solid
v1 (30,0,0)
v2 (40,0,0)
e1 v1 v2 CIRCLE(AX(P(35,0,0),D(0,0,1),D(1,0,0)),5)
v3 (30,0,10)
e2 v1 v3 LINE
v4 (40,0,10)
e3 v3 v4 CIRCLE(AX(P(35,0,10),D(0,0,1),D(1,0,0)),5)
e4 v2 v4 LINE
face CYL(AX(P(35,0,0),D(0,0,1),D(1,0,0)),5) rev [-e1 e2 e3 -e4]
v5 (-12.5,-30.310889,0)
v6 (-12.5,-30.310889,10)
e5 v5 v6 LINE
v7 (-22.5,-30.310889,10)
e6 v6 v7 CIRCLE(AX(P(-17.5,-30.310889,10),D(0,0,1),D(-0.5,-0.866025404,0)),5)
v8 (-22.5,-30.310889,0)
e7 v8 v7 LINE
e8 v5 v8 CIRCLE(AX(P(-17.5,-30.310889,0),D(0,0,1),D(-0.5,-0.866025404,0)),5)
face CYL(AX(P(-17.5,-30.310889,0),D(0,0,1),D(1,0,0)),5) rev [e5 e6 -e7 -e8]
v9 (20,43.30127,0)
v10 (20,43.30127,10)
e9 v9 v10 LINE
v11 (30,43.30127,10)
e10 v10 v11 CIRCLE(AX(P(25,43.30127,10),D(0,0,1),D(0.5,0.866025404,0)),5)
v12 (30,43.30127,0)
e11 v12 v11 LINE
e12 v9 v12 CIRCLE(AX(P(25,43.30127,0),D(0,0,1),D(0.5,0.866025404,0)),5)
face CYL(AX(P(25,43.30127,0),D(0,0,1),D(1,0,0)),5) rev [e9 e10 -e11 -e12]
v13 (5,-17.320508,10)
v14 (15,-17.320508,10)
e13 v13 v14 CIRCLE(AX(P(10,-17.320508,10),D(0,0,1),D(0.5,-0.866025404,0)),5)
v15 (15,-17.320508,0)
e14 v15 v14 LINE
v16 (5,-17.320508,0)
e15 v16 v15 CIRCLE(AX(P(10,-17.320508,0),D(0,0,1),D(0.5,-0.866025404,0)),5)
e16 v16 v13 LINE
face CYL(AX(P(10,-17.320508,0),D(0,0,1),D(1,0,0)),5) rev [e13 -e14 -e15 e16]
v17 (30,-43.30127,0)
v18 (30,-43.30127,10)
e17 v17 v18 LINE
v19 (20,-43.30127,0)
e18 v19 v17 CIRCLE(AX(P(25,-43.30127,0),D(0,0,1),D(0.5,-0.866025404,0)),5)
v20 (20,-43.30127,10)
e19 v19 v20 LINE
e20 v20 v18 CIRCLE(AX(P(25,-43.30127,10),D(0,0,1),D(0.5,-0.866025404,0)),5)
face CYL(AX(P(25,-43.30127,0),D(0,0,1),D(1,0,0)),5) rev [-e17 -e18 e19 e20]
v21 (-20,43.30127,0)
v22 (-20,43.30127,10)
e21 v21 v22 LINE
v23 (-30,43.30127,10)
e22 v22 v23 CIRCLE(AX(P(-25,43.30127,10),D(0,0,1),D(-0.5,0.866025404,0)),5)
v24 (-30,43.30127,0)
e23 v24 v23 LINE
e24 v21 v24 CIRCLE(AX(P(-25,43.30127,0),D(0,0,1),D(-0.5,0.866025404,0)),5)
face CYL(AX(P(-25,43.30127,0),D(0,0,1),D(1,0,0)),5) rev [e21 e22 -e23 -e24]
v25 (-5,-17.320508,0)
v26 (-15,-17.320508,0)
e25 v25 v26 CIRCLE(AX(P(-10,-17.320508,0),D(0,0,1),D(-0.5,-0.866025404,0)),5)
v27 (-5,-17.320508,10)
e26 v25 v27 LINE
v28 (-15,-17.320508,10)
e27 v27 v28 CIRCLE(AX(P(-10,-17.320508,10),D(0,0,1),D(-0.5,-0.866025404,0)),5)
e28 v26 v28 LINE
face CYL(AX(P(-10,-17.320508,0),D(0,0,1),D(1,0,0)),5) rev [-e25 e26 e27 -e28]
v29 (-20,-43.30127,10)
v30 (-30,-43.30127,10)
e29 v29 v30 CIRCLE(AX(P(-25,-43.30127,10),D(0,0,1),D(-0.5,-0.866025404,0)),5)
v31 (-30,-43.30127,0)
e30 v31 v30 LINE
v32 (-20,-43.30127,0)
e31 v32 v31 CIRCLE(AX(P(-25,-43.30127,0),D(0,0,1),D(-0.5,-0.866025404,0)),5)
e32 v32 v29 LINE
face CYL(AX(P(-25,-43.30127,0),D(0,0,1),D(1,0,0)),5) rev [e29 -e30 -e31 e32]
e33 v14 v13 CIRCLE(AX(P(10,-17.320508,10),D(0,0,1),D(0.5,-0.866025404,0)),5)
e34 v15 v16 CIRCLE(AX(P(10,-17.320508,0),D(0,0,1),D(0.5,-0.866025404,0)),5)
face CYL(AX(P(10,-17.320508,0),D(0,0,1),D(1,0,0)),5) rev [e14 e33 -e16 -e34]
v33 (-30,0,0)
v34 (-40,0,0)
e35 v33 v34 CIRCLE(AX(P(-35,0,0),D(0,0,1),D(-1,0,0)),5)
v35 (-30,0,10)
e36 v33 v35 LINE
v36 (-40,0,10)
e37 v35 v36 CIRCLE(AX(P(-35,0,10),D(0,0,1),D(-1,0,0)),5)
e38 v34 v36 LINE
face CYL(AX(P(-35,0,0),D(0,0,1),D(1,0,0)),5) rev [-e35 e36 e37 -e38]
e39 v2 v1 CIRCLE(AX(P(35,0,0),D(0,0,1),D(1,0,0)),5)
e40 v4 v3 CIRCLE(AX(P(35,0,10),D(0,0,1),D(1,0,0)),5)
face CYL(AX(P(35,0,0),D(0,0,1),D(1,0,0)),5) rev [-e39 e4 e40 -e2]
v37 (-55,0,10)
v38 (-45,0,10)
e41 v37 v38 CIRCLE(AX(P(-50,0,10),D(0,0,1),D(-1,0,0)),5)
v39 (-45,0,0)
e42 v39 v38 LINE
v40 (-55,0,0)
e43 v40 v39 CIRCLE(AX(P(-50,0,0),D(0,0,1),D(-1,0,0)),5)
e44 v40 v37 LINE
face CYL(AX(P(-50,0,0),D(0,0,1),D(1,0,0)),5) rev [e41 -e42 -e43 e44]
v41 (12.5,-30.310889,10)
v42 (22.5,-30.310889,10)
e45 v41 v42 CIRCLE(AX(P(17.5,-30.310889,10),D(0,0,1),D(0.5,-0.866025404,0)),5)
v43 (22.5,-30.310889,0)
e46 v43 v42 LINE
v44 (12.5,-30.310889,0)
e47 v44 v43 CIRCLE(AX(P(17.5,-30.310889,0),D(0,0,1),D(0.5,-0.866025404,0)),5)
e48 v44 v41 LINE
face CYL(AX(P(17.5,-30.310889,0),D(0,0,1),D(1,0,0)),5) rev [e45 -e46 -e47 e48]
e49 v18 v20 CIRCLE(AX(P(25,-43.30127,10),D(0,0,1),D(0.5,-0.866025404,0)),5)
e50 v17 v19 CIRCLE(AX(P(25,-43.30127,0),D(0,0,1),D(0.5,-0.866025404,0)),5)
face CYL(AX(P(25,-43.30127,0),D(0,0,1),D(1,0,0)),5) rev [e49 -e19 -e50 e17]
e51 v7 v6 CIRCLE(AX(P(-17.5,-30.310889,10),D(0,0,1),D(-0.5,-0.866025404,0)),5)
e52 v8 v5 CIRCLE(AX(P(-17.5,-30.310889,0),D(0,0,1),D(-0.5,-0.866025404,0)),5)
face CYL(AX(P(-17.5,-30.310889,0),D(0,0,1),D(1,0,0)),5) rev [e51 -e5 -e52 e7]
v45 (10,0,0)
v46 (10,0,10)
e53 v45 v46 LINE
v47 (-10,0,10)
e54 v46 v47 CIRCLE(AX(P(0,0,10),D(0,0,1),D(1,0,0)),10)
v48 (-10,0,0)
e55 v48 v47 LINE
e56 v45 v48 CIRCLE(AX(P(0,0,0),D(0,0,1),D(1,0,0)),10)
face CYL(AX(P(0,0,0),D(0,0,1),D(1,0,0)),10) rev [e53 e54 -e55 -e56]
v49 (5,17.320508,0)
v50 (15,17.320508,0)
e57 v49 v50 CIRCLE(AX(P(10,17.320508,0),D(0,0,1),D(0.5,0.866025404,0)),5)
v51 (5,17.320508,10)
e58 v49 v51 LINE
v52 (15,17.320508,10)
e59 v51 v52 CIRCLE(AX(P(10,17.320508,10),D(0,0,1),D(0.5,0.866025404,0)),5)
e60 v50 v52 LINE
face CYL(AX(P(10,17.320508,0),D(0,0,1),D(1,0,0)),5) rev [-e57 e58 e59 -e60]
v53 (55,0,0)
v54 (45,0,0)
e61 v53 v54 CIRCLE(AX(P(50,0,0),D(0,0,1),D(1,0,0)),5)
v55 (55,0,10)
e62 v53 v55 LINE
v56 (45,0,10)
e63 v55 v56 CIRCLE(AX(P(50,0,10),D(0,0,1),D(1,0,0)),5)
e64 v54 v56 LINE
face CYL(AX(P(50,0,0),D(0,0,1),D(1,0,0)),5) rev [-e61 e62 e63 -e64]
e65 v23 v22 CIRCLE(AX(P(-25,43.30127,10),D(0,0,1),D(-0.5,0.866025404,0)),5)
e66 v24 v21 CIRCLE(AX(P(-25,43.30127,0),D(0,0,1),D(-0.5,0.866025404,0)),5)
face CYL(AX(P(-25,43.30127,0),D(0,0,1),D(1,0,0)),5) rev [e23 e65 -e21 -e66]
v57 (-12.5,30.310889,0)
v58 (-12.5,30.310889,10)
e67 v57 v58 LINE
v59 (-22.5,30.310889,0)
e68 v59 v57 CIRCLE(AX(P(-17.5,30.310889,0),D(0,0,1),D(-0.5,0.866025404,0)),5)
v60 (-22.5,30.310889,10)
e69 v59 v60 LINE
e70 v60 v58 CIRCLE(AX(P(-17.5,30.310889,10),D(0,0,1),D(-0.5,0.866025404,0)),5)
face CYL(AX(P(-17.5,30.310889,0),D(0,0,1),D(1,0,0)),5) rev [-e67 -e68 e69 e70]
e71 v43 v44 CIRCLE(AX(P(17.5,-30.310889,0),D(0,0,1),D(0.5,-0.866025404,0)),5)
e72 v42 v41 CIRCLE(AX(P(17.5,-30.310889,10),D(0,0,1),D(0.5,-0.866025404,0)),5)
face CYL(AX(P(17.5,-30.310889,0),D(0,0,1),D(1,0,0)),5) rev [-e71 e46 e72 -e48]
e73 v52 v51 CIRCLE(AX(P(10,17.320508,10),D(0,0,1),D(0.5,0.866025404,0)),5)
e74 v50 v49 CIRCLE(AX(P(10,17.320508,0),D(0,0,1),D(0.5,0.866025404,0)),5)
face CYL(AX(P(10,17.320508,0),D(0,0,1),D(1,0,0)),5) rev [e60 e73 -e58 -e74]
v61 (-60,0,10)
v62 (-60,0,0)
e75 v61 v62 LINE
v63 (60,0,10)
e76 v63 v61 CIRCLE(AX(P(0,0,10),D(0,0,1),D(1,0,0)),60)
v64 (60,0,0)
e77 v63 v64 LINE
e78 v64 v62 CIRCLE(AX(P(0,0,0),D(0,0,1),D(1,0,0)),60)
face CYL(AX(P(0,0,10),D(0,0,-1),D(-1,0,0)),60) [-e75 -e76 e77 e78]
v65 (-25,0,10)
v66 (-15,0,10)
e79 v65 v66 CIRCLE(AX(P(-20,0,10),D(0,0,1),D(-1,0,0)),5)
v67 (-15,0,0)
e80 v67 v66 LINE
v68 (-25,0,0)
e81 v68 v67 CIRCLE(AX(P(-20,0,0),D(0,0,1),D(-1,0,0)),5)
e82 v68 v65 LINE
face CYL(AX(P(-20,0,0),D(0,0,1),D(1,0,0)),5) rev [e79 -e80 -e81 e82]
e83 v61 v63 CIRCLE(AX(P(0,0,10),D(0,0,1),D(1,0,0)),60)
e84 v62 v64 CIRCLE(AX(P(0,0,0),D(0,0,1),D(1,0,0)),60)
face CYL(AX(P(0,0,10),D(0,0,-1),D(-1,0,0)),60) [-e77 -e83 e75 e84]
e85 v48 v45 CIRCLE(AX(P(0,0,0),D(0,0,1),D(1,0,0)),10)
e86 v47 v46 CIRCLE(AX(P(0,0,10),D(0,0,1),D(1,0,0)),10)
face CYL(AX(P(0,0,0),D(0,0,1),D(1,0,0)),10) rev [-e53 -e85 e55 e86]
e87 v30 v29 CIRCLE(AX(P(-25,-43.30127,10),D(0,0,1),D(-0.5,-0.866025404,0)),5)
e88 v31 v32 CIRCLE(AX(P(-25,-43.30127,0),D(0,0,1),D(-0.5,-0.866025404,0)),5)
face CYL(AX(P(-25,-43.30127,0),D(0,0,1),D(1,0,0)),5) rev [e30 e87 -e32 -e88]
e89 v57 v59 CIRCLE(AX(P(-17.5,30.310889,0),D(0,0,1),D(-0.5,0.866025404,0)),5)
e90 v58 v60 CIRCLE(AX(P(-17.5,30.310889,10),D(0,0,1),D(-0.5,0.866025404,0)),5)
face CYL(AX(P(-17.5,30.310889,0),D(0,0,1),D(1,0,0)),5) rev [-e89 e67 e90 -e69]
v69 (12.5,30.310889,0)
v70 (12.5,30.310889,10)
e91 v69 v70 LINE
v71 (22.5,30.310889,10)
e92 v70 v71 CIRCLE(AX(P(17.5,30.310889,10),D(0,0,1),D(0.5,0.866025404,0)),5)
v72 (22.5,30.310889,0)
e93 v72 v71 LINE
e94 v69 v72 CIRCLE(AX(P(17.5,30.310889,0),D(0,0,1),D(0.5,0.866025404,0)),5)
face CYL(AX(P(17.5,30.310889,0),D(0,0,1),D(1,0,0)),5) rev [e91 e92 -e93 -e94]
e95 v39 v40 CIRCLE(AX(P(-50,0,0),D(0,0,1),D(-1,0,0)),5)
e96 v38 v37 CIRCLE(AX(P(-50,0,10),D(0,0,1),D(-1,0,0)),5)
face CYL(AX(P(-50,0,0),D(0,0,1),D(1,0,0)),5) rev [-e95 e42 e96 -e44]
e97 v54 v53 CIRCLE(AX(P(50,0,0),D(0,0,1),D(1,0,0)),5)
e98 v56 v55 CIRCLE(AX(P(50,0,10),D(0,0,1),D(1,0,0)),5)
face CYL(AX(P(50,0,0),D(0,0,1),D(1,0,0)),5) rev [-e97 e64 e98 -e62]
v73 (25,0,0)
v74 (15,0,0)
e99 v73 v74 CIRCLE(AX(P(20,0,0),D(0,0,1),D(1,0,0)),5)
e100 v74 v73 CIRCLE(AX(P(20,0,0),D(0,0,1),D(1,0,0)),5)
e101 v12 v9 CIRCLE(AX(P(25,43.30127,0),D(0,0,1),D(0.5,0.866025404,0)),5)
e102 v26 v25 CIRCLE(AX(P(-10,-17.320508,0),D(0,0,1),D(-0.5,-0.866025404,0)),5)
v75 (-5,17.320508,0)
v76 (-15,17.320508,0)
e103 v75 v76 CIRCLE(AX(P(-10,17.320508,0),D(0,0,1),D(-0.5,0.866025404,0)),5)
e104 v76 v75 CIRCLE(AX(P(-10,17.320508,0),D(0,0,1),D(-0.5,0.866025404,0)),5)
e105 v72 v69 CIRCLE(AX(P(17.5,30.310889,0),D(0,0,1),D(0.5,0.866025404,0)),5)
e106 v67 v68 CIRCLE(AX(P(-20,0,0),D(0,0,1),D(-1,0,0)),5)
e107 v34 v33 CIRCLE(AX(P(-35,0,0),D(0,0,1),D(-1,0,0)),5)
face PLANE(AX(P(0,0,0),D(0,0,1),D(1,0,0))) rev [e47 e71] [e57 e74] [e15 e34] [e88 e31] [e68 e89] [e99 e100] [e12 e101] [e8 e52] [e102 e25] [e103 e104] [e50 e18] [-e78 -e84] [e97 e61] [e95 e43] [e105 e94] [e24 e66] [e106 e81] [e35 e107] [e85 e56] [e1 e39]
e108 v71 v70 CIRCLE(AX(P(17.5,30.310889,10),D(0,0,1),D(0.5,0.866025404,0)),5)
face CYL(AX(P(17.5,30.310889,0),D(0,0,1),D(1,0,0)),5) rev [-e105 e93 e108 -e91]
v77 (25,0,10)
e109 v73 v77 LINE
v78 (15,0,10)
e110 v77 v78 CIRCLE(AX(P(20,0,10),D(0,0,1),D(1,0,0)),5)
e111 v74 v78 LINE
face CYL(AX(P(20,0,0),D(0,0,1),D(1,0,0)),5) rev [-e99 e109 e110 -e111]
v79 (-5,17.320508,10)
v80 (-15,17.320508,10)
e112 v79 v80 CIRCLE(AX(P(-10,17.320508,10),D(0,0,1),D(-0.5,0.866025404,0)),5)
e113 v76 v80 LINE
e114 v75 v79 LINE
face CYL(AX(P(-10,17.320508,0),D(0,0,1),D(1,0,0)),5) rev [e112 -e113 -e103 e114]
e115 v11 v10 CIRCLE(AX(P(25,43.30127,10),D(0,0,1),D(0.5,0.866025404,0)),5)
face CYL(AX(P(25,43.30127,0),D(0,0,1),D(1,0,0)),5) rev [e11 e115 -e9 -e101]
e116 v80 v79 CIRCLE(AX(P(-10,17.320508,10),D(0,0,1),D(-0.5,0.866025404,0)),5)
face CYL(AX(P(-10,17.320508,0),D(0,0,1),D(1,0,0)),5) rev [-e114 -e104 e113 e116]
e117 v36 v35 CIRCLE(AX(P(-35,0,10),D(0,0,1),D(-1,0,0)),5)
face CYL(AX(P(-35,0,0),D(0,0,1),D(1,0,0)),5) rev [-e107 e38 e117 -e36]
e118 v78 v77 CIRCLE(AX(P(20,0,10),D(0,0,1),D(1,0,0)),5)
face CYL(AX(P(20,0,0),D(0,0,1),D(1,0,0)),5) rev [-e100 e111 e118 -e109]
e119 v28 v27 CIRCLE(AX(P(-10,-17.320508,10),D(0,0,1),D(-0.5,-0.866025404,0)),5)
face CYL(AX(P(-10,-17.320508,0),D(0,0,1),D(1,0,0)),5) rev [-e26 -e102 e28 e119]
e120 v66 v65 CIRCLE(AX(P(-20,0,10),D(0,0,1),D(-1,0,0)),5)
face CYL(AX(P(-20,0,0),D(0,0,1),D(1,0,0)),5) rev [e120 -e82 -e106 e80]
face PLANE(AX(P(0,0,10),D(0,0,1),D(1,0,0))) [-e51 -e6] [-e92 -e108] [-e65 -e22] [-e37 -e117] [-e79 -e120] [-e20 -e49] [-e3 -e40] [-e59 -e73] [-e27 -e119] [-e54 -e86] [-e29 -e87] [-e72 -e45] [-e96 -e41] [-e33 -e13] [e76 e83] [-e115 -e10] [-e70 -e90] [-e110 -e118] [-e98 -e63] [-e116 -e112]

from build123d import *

# Parameters (mm, degrees)
FLANGE_OUTLINE_120_R                 = 60
FLANGE_DISC_DEPTH                    = 10
CENTRE_BORE_PROFILE_20_R             = 10
CENTRE_BORE_20_DEPTH                 = 10
SEED_HOLE_PROFILE_10_R               = 5
SEED_HOLE_10_DEPTH                   = 10
SEED_HOLE_CIRCULAR_PATTERN_6X_COUNT  = 6
RADIAL_HOLE_ROW_3X_COUNT             = 3
RADIAL_HOLE_ROW_3X_PITCH             = 15
RADIAL_HOLE_ROWS_6X_COPY_1_SKETCH_R  = 5
RADIAL_HOLE_ROWS_6X_COPY_1_DEPTH     = 10
RADIAL_HOLE_ROWS_6X_COPY_2_SKETCH_R  = 5
RADIAL_HOLE_ROWS_6X_COPY_2_DEPTH     = 10
RADIAL_HOLE_ROWS_6X_COPY_3_SKETCH_R  = 5
RADIAL_HOLE_ROWS_6X_COPY_3_DEPTH     = 10
RADIAL_HOLE_ROWS_6X_COPY_4_SKETCH_R  = 5
RADIAL_HOLE_ROWS_6X_COPY_4_DEPTH     = 10
RADIAL_HOLE_ROWS_6X_COPY_5_SKETCH_R  = 5
RADIAL_HOLE_ROWS_6X_COPY_5_DEPTH     = 10
RADIAL_HOLE_ROWS_6X_COPY_6_SKETCH_R  = 5
RADIAL_HOLE_ROWS_6X_COPY_6_DEPTH     = 10
RADIAL_HOLE_ROWS_6X_COPY_7_SKETCH_R  = 5
RADIAL_HOLE_ROWS_6X_COPY_7_DEPTH     = 10
RADIAL_HOLE_ROWS_6X_COPY_8_SKETCH_R  = 5
RADIAL_HOLE_ROWS_6X_COPY_8_DEPTH     = 10
RADIAL_HOLE_ROWS_6X_COPY_9_SKETCH_R  = 5
RADIAL_HOLE_ROWS_6X_COPY_9_DEPTH     = 10
RADIAL_HOLE_ROWS_6X_COPY_10_SKETCH_R = 5
RADIAL_HOLE_ROWS_6X_COPY_10_DEPTH    = 10
RADIAL_HOLE_ROWS_6X_COPY_11_SKETCH_R = 5
RADIAL_HOLE_ROWS_6X_COPY_11_DEPTH    = 10
RADIAL_HOLE_ROWS_6X_COPY_12_SKETCH_R = 5
RADIAL_HOLE_ROWS_6X_COPY_12_DEPTH    = 10
RADIAL_HOLE_ROWS_6X_COPY_13_SKETCH_R = 5
RADIAL_HOLE_ROWS_6X_COPY_13_DEPTH    = 10
RADIAL_HOLE_ROWS_6X_COPY_14_SKETCH_R = 5
RADIAL_HOLE_ROWS_6X_COPY_14_DEPTH    = 10
RADIAL_HOLE_ROWS_6X_COPY_15_SKETCH_R = 5
RADIAL_HOLE_ROWS_6X_COPY_15_DEPTH    = 10


with BuildPart() as part:
    # Flange Outline Ø120 → Flange Disc (new body)
    with BuildSketch(Plane.XY):
        Circle(FLANGE_OUTLINE_120_R)
    extrude(amount=FLANGE_DISC_DEPTH)

    # Centre Bore Profile Ø20 → Centre Bore Ø20 (cut)
    with BuildSketch(Plane.XY.offset(10)):
        Circle(CENTRE_BORE_PROFILE_20_R)
    extrude(amount=-CENTRE_BORE_20_DEPTH, mode=Mode.SUBTRACT)

    # Seed Hole Profile Ø10 → Seed Hole Ø10 (cut)
    with BuildSketch(Plane.XY.offset(10)):
        with Locations((20, 0)):
            Circle(SEED_HOLE_PROFILE_10_R)
    seed_hole_10 = extrude(amount=-SEED_HOLE_10_DEPTH, mode=Mode.SUBTRACT)

    # Seed Hole Circular Pattern 6x: Seed Hole Ø10 ×6 about axis
    seed_hole_circular_pattern_6x_axis = Axis((0, 0, 0), (0, 0, 1))
    for i in range(1, SEED_HOLE_CIRCULAR_PATTERN_6X_COUNT):
        add(seed_hole_10.rotate(seed_hole_circular_pattern_6x_axis, i * 360 / SEED_HOLE_CIRCULAR_PATTERN_6X_COUNT), mode=Mode.SUBTRACT)

    # Radial Hole Row 3x: Seed Hole Ø10 ×3
    with Locations(*[(i * RADIAL_HOLE_ROW_3X_PITCH, 0, 0) for i in range(1, RADIAL_HOLE_ROW_3X_COUNT)]):
        add(seed_hole_10, mode=Mode.SUBTRACT)

    # Radial Hole Rows 6x copy 1 sketch → Radial Hole Rows 6x copy 1 (cut)
    with BuildSketch(Plane(origin=(7.5, 12.990381057, 10), x_dir=(0.5000000000000001, 0.8660254037844386, 0), z_dir=(0, 0, 1))):
        with Locations((20, 0)):
            Circle(RADIAL_HOLE_ROWS_6X_COPY_1_SKETCH_R)
    extrude(amount=-RADIAL_HOLE_ROWS_6X_COPY_1_DEPTH, mode=Mode.SUBTRACT)

    # Radial Hole Rows 6x copy 2 sketch → Radial Hole Rows 6x copy 2 (cut)
    with BuildSketch(Plane(origin=(-7.5, 12.990381057, 10), x_dir=(-0.4999999999999998, 0.8660254037844387, 0), z_dir=(0, 0, 1))):
        with Locations((20, 0)):
            Circle(RADIAL_HOLE_ROWS_6X_COPY_2_SKETCH_R)
    extrude(amount=-RADIAL_HOLE_ROWS_6X_COPY_2_DEPTH, mode=Mode.SUBTRACT)

    # Radial Hole Rows 6x copy 3 sketch → Radial Hole Rows 6x copy 3 (cut)
    with BuildSketch(Plane(origin=(-15, 0, 10), x_dir=(-1, 0, 0), z_dir=(0, 0, 1))):
        with Locations((20, 0)):
            Circle(RADIAL_HOLE_ROWS_6X_COPY_3_SKETCH_R)
    extrude(amount=-RADIAL_HOLE_ROWS_6X_COPY_3_DEPTH, mode=Mode.SUBTRACT)

    # Radial Hole Rows 6x copy 4 sketch → Radial Hole Rows 6x copy 4 (cut)
    with BuildSketch(Plane(origin=(-7.5, -12.990381057, 10), x_dir=(-0.5000000000000004, -0.8660254037844384, 0), z_dir=(0, 0, 1))):
        with Locations((20, 0)):
            Circle(RADIAL_HOLE_ROWS_6X_COPY_4_SKETCH_R)
    extrude(amount=-RADIAL_HOLE_ROWS_6X_COPY_4_DEPTH, mode=Mode.SUBTRACT)

    # Radial Hole Rows 6x copy 5 sketch → Radial Hole Rows 6x copy 5 (cut)
    with BuildSketch(Plane(origin=(7.5, -12.990381057, 10), x_dir=(0.5000000000000001, -0.8660254037844386, 0), z_dir=(0, 0, 1))):
        with Locations((20, 0)):
            Circle(RADIAL_HOLE_ROWS_6X_COPY_5_SKETCH_R)
    extrude(amount=-RADIAL_HOLE_ROWS_6X_COPY_5_DEPTH, mode=Mode.SUBTRACT)

    # Radial Hole Rows 6x copy 6 sketch → Radial Hole Rows 6x copy 6 (cut)
    with BuildSketch(Plane(origin=(15, 25.980762114, 10), x_dir=(0.5000000000000001, 0.8660254037844386, 0), z_dir=(0, 0, 1))):
        with Locations((20, 0)):
            Circle(RADIAL_HOLE_ROWS_6X_COPY_6_SKETCH_R)
    extrude(amount=-RADIAL_HOLE_ROWS_6X_COPY_6_DEPTH, mode=Mode.SUBTRACT)

    # Radial Hole Rows 6x copy 7 sketch → Radial Hole Rows 6x copy 7 (cut)
    with BuildSketch(Plane(origin=(-15, 25.980762114, 10), x_dir=(-0.4999999999999998, 0.8660254037844387, 0), z_dir=(0, 0, 1))):
        with Locations((20, 0)):
            Circle(RADIAL_HOLE_ROWS_6X_COPY_7_SKETCH_R)
    extrude(amount=-RADIAL_HOLE_ROWS_6X_COPY_7_DEPTH, mode=Mode.SUBTRACT)

    # Radial Hole Rows 6x copy 8 sketch → Radial Hole Rows 6x copy 8 (cut)
    with BuildSketch(Plane(origin=(-30, 0, 10), x_dir=(-1, 0, 0), z_dir=(0, 0, 1))):
        with Locations((20, 0)):
            Circle(RADIAL_HOLE_ROWS_6X_COPY_8_SKETCH_R)
    extrude(amount=-RADIAL_HOLE_ROWS_6X_COPY_8_DEPTH, mode=Mode.SUBTRACT)

    # Radial Hole Rows 6x copy 9 sketch → Radial Hole Rows 6x copy 9 (cut)
    with BuildSketch(Plane(origin=(-15, -25.980762114, 10), x_dir=(-0.5000000000000004, -0.8660254037844384, 0), z_dir=(0, 0, 1))):
        with Locations((20, 0)):
            Circle(RADIAL_HOLE_ROWS_6X_COPY_9_SKETCH_R)
    extrude(amount=-RADIAL_HOLE_ROWS_6X_COPY_9_DEPTH, mode=Mode.SUBTRACT)

    # Radial Hole Rows 6x copy 10 sketch → Radial Hole Rows 6x copy 10 (cut)
    with BuildSketch(Plane(origin=(15, -25.980762114, 10), x_dir=(0.5000000000000001, -0.8660254037844386, 0), z_dir=(0, 0, 1))):
        with Locations((20, 0)):
            Circle(RADIAL_HOLE_ROWS_6X_COPY_10_SKETCH_R)
    extrude(amount=-RADIAL_HOLE_ROWS_6X_COPY_10_DEPTH, mode=Mode.SUBTRACT)

    # Radial Hole Rows 6x copy 11 sketch → Radial Hole Rows 6x copy 11 (cut)
    with BuildSketch(Plane(origin=(0, 0, 10), x_dir=(0.5000000000000001, 0.8660254037844386, 0), z_dir=(0, 0, 1))):
        with Locations((20, 0)):
            Circle(RADIAL_HOLE_ROWS_6X_COPY_11_SKETCH_R)
    extrude(amount=-RADIAL_HOLE_ROWS_6X_COPY_11_DEPTH, mode=Mode.SUBTRACT)

    # Radial Hole Rows 6x copy 12 sketch → Radial Hole Rows 6x copy 12 (cut)
    with BuildSketch(Plane(origin=(0, 0, 10), x_dir=(-0.4999999999999998, 0.8660254037844387, 0), z_dir=(0, 0, 1))):
        with Locations((20, 0)):
            Circle(RADIAL_HOLE_ROWS_6X_COPY_12_SKETCH_R)
    extrude(amount=-RADIAL_HOLE_ROWS_6X_COPY_12_DEPTH, mode=Mode.SUBTRACT)

    # Radial Hole Rows 6x copy 13 sketch → Radial Hole Rows 6x copy 13 (cut)
    with BuildSketch(Plane(origin=(0, 0, 10), x_dir=(-1, 0, 0), z_dir=(0, 0, 1))):
        with Locations((20, 0)):
            Circle(RADIAL_HOLE_ROWS_6X_COPY_13_SKETCH_R)
    extrude(amount=-RADIAL_HOLE_ROWS_6X_COPY_13_DEPTH, mode=Mode.SUBTRACT)

    # Radial Hole Rows 6x copy 14 sketch → Radial Hole Rows 6x copy 14 (cut)
    with BuildSketch(Plane(origin=(0, 0, 10), x_dir=(-0.5000000000000004, -0.8660254037844384, 0), z_dir=(0, 0, 1))):
        with Locations((20, 0)):
            Circle(RADIAL_HOLE_ROWS_6X_COPY_14_SKETCH_R)
    extrude(amount=-RADIAL_HOLE_ROWS_6X_COPY_14_DEPTH, mode=Mode.SUBTRACT)

    # Radial Hole Rows 6x copy 15 sketch → Radial Hole Rows 6x copy 15 (cut)
    with BuildSketch(Plane(origin=(0, 0, 10), x_dir=(0.5000000000000001, -0.8660254037844386, 0), z_dir=(0, 0, 1))):
        with Locations((20, 0)):
            Circle(RADIAL_HOLE_ROWS_6X_COPY_15_SKETCH_R)
    extrude(amount=-RADIAL_HOLE_ROWS_6X_COPY_15_DEPTH, mode=Mode.SUBTRACT)


solid = part.part
